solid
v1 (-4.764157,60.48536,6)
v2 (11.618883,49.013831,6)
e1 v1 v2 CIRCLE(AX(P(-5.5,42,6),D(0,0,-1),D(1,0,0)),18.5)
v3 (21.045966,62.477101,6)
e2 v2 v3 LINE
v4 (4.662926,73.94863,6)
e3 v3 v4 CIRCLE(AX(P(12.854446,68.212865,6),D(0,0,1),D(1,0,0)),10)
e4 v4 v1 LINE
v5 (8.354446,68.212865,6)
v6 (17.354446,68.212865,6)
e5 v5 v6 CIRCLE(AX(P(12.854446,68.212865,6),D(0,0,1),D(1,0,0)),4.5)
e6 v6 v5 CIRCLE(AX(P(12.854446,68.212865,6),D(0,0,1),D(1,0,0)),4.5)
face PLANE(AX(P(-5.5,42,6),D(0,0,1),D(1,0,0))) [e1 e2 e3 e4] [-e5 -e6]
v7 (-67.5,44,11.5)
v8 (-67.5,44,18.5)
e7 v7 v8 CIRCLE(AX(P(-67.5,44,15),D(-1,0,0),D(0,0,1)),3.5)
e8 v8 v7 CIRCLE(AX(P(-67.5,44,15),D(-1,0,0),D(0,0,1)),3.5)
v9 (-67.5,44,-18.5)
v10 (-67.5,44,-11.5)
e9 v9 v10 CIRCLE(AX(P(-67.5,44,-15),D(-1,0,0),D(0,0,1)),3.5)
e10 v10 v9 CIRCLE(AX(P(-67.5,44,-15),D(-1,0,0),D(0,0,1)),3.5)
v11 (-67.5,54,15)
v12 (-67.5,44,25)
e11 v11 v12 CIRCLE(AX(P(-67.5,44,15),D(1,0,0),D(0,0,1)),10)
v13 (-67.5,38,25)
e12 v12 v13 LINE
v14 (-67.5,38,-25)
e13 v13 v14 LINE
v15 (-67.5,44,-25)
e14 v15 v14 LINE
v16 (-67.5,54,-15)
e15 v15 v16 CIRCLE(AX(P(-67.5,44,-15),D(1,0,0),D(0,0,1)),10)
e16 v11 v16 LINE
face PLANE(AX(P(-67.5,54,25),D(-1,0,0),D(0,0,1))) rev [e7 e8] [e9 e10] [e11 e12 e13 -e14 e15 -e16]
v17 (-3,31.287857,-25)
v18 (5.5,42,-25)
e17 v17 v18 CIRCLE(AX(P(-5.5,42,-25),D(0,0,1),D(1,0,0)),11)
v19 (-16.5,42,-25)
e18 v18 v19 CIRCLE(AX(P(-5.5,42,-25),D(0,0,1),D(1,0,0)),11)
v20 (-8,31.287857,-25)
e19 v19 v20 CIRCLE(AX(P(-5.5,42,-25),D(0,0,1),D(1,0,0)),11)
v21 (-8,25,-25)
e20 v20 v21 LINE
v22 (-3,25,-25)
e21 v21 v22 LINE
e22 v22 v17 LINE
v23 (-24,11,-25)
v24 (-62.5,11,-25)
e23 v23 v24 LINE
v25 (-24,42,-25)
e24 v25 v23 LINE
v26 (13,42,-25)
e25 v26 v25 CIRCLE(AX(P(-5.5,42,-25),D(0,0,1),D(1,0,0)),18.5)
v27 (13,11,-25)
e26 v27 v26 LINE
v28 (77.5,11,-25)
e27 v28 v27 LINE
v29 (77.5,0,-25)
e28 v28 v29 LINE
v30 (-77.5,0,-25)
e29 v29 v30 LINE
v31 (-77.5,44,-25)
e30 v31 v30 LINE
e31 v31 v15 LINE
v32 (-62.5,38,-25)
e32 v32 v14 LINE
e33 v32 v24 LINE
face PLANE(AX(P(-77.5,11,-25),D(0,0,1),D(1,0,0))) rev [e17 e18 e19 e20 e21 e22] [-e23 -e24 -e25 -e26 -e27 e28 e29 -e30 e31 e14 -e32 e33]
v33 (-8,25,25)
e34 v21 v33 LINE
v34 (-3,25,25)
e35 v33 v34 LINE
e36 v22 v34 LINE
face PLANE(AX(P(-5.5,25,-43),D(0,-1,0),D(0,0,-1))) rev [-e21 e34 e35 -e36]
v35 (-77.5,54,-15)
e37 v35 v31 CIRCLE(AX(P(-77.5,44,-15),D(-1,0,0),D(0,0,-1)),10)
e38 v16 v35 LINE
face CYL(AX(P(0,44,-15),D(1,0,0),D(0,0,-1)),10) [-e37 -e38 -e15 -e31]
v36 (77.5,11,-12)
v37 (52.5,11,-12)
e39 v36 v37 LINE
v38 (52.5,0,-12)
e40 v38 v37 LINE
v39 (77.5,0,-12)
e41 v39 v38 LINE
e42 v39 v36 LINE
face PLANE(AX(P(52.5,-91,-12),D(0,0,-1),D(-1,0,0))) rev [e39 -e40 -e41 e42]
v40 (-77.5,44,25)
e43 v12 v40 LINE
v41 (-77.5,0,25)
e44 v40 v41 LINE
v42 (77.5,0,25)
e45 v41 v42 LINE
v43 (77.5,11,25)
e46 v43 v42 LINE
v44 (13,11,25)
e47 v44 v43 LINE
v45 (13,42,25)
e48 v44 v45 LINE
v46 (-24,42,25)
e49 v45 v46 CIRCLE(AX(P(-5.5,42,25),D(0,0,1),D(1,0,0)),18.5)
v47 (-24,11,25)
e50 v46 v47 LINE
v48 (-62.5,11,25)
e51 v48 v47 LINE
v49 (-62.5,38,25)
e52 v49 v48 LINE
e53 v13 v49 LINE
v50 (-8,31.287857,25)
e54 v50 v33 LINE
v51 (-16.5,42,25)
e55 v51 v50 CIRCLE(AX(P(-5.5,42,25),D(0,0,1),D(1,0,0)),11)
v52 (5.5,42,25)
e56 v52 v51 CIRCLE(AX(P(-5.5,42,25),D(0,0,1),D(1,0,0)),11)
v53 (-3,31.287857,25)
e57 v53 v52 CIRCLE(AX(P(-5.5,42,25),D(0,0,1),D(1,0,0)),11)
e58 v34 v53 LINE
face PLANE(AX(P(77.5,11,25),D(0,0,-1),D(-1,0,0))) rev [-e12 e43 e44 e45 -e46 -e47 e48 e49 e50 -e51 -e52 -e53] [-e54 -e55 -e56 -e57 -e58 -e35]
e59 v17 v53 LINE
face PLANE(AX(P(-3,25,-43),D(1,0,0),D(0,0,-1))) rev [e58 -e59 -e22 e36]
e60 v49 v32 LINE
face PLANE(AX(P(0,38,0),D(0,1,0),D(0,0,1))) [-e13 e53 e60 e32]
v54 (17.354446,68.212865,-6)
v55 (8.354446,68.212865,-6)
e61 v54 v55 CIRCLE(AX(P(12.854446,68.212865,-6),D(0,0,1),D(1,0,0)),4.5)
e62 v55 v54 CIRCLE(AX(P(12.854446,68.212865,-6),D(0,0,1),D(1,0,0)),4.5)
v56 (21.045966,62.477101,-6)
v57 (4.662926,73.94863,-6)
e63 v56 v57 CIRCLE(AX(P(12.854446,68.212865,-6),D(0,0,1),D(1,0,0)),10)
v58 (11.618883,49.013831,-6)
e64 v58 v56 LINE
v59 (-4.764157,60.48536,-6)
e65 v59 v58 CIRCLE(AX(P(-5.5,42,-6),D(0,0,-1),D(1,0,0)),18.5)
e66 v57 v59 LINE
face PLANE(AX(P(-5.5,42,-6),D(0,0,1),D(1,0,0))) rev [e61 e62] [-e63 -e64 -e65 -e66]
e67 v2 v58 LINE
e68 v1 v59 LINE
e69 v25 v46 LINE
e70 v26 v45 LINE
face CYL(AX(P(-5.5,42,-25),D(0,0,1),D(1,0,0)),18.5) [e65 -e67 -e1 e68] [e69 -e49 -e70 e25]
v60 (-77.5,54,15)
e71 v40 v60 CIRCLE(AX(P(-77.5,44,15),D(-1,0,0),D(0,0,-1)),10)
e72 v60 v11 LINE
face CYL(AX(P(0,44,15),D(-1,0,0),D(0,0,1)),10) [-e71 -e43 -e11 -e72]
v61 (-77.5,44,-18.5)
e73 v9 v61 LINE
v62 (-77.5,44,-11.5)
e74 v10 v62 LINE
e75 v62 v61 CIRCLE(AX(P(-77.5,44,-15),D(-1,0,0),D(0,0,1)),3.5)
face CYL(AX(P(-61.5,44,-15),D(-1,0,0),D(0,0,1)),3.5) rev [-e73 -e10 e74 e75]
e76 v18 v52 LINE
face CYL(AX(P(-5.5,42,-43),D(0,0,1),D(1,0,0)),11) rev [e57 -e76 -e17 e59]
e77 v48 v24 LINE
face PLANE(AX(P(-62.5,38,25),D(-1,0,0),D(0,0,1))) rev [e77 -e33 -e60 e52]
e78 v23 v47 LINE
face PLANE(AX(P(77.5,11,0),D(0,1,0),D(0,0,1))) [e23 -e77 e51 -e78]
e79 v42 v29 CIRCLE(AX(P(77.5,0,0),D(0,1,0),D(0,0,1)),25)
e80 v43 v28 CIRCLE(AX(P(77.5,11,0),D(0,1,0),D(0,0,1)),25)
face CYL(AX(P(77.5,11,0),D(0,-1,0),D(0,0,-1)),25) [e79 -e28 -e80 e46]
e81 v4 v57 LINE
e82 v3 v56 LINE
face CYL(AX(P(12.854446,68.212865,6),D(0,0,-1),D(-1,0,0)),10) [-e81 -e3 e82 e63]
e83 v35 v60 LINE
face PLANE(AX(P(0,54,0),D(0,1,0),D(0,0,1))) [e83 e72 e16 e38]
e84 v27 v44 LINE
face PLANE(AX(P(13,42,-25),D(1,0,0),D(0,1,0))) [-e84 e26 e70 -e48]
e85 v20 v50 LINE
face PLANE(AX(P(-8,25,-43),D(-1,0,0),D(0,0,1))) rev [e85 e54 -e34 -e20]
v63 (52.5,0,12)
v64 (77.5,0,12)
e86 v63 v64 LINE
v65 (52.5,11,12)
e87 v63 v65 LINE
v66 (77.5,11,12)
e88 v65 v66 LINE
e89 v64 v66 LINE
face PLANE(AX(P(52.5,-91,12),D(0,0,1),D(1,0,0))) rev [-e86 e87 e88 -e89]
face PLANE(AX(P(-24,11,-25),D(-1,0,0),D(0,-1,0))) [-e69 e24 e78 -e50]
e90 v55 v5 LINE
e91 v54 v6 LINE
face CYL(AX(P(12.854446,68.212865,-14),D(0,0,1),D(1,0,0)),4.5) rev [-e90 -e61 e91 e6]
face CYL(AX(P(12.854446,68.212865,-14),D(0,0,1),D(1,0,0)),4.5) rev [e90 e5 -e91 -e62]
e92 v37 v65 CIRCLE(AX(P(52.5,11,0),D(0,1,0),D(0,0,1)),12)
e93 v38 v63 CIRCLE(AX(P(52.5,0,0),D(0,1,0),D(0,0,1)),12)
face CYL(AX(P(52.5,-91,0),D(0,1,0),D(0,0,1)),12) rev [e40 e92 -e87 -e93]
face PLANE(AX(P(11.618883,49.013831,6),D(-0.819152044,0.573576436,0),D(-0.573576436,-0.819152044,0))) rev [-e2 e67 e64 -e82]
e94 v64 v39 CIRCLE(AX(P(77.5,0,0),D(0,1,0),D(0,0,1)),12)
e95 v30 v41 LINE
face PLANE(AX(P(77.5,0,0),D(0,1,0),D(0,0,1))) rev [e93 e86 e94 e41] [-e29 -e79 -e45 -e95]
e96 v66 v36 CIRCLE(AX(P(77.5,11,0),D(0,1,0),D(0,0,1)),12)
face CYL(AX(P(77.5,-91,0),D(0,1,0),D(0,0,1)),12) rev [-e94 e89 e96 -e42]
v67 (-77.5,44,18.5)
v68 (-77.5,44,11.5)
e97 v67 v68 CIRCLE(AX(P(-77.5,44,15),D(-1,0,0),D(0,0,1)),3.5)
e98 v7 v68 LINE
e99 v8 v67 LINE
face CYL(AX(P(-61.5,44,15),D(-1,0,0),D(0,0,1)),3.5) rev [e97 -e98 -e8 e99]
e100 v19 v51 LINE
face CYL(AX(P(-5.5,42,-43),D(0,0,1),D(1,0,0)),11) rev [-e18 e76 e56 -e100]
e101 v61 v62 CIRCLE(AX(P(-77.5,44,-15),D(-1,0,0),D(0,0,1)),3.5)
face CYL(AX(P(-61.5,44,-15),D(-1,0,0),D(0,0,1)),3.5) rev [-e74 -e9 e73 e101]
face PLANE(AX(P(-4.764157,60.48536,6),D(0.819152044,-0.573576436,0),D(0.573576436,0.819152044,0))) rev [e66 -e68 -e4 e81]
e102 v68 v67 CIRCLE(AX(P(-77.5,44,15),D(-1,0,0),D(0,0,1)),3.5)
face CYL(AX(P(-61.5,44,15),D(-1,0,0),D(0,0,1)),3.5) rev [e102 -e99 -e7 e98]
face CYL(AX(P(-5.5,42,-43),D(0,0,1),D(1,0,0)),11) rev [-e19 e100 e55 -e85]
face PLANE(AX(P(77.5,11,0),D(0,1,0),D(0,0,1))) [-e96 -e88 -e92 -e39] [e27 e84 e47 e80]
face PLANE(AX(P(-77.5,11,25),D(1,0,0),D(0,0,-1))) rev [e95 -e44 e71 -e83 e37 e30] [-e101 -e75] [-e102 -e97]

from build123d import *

# Parameters (mm, degrees)
BASE_PLATE_11MM_DEPTH   = 11
CHANNEL_CUT_12X25_DEPTH = 102
BORE_BLOCK_DEPTH        = 50
KEYED_BORE_11_DEPTH     = 68
ANGLED_LUG_DEPTH        = 6
LUG_HOLE_SKETCH_R       = 4.5
LUG_HOLE_9_DEPTH        = 20
END_LUG_SKETCH_W        = 15
END_LUG_SKETCH_H        = 50
END_LUG_DEPTH           = 27
END_LUG_TIP_SKETCH_W    = 10
END_LUG_TIP_SKETCH_H    = 50
END_LUG_TIP_DEPTH       = 16
END_LUG_ROUND_R10_A_R   = 10
END_LUG_ROUND_R10_B_R   = 10
END_LUG_CUT_SKETCH_R    = 3.5
END_LUG_CUT_7_DEPTH     = 16


with BuildPart() as part:
    # Base Plate Sketch → Base Plate 11mm (new body)
    with BuildSketch(Plane(origin=(0, 0, 0), x_dir=(1, 0, 0), z_dir=(0, 1, 0))):
        with BuildLine():
            Line((77.5, -25), (-77.5, -25))
            Line((-77.5, -25), (-77.5, 25))
            Line((-77.5, 25), (77.5, 25))
            ThreePointArc((77.5, 25), (102.5, 0), (77.5, -25))
        make_face()
    extrude(amount=BASE_PLATE_11MM_DEPTH)

    # Channel Cut Sketch → Channel Cut 12x25 (cut)
    with BuildSketch(Plane(origin=(0, 11, 0), x_dir=(1, 0, 0), z_dir=(0, 1, 0))):
        with BuildLine():
            Line((52.5, 12), (77.5, 12))
            ThreePointArc((77.5, 12), (89.5, 0), (77.5, -12))
            Line((77.5, -12), (52.5, -12))
            ThreePointArc((52.5, -12), (40.5, 0), (52.5, 12))
        make_face()
    extrude(amount=-CHANNEL_CUT_12X25_DEPTH, mode=Mode.SUBTRACT)

    # Bore Block Sketch → Bore Block (add)
    with BuildSketch(Plane.XY.offset(25)):
        with BuildLine():
            Line((-24, 11), (13, 11))
            Line((13, 11), (13, 42))
            ThreePointArc((13, 42), (-5.5, 60.5), (-24, 42))
            Line((-24, 42), (-24, 11))
        make_face()
    extrude(amount=-BORE_BLOCK_DEPTH)

    # Keyed Bore Sketch → Keyed Bore Ø11 (cut)
    with BuildSketch(Plane.XY.offset(25)):
        with BuildLine():
            Line((-5.5, 25), (-3, 25))
            Line((-3, 25), (-3, 31.287857357))
            ThreePointArc((-3, 31.287857357), (-5.5, 53), (-8, 31.287857357))
            Line((-8, 31.287857357), (-8, 25))
            Line((-8, 25), (-5.5, 25))
        make_face()
    extrude(amount=-KEYED_BORE_11_DEPTH, mode=Mode.SUBTRACT)

    # Angled Lug Sketch → Angled Lug (add, symmetric)
    with BuildSketch(Plane.XY):
        with BuildLine():
            Line((11.618883443, 49.013831311), (21.045966406, 62.477101054))
            ThreePointArc((21.045966406, 62.477101054), (18.590210327, 76.40438586), (4.66292552, 73.948629781))
            Line((4.66292552, 73.948629781), (-4.764157443, 60.485360038))
            ThreePointArc((-4.764157443, 60.485360038), (5.111164072, 57.154312819), (11.618883443, 49.013831311))
        make_face()
    extrude(amount=ANGLED_LUG_DEPTH, both=True)

    # Lug Hole Sketch → Lug Hole Ø9 (cut)
    with BuildSketch(Plane.XY.offset(6)):
        with Locations((12.854445963, 68.212865417)):
            Circle(LUG_HOLE_SKETCH_R)
    extrude(amount=-LUG_HOLE_9_DEPTH, mode=Mode.SUBTRACT)

    # End Lug Sketch → End Lug (add)
    with BuildSketch(Plane(origin=(0, 11, 0), x_dir=(1, 0, 0), z_dir=(0, 1, 0))):
        with Locations((-70, 0)):
            Rectangle(END_LUG_SKETCH_W, END_LUG_SKETCH_H)
    extrude(amount=END_LUG_DEPTH)

    # End Lug Tip Sketch → End Lug Tip (add)
    with BuildSketch(Plane(origin=(0, 38, 0), x_dir=(1, 0, 0), z_dir=(0, 1, 0))):
        with Locations((-72.5, 0)):
            Rectangle(END_LUG_TIP_SKETCH_W, END_LUG_TIP_SKETCH_H)
    extrude(amount=END_LUG_TIP_DEPTH)

    # End Lug Round R10 A
    end_lug_round_r10_a_edges = [part.edges().sort_by_distance(p)[0] for p in [
        (-72.5, 54, 25),
    ]]
    fillet(end_lug_round_r10_a_edges, radius=END_LUG_ROUND_R10_A_R)

    # End Lug Round R10 B
    end_lug_round_r10_b_edges = [part.edges().sort_by_distance(p)[0] for p in [
        (-72.5, 54, -25),
    ]]
    fillet(end_lug_round_r10_b_edges, radius=END_LUG_ROUND_R10_B_R)

    # End Lug Cut Sketch → End Lug Cut Ø7 (cut)
    with BuildSketch(Plane.ZY.offset(77.5)):
        with Locations((15, 44)):
            Circle(END_LUG_CUT_SKETCH_R)
        with Locations((-15, 44)):
            Circle(END_LUG_CUT_SKETCH_R)
    extrude(amount=-END_LUG_CUT_7_DEPTH, mode=Mode.SUBTRACT)


solid = part.part
